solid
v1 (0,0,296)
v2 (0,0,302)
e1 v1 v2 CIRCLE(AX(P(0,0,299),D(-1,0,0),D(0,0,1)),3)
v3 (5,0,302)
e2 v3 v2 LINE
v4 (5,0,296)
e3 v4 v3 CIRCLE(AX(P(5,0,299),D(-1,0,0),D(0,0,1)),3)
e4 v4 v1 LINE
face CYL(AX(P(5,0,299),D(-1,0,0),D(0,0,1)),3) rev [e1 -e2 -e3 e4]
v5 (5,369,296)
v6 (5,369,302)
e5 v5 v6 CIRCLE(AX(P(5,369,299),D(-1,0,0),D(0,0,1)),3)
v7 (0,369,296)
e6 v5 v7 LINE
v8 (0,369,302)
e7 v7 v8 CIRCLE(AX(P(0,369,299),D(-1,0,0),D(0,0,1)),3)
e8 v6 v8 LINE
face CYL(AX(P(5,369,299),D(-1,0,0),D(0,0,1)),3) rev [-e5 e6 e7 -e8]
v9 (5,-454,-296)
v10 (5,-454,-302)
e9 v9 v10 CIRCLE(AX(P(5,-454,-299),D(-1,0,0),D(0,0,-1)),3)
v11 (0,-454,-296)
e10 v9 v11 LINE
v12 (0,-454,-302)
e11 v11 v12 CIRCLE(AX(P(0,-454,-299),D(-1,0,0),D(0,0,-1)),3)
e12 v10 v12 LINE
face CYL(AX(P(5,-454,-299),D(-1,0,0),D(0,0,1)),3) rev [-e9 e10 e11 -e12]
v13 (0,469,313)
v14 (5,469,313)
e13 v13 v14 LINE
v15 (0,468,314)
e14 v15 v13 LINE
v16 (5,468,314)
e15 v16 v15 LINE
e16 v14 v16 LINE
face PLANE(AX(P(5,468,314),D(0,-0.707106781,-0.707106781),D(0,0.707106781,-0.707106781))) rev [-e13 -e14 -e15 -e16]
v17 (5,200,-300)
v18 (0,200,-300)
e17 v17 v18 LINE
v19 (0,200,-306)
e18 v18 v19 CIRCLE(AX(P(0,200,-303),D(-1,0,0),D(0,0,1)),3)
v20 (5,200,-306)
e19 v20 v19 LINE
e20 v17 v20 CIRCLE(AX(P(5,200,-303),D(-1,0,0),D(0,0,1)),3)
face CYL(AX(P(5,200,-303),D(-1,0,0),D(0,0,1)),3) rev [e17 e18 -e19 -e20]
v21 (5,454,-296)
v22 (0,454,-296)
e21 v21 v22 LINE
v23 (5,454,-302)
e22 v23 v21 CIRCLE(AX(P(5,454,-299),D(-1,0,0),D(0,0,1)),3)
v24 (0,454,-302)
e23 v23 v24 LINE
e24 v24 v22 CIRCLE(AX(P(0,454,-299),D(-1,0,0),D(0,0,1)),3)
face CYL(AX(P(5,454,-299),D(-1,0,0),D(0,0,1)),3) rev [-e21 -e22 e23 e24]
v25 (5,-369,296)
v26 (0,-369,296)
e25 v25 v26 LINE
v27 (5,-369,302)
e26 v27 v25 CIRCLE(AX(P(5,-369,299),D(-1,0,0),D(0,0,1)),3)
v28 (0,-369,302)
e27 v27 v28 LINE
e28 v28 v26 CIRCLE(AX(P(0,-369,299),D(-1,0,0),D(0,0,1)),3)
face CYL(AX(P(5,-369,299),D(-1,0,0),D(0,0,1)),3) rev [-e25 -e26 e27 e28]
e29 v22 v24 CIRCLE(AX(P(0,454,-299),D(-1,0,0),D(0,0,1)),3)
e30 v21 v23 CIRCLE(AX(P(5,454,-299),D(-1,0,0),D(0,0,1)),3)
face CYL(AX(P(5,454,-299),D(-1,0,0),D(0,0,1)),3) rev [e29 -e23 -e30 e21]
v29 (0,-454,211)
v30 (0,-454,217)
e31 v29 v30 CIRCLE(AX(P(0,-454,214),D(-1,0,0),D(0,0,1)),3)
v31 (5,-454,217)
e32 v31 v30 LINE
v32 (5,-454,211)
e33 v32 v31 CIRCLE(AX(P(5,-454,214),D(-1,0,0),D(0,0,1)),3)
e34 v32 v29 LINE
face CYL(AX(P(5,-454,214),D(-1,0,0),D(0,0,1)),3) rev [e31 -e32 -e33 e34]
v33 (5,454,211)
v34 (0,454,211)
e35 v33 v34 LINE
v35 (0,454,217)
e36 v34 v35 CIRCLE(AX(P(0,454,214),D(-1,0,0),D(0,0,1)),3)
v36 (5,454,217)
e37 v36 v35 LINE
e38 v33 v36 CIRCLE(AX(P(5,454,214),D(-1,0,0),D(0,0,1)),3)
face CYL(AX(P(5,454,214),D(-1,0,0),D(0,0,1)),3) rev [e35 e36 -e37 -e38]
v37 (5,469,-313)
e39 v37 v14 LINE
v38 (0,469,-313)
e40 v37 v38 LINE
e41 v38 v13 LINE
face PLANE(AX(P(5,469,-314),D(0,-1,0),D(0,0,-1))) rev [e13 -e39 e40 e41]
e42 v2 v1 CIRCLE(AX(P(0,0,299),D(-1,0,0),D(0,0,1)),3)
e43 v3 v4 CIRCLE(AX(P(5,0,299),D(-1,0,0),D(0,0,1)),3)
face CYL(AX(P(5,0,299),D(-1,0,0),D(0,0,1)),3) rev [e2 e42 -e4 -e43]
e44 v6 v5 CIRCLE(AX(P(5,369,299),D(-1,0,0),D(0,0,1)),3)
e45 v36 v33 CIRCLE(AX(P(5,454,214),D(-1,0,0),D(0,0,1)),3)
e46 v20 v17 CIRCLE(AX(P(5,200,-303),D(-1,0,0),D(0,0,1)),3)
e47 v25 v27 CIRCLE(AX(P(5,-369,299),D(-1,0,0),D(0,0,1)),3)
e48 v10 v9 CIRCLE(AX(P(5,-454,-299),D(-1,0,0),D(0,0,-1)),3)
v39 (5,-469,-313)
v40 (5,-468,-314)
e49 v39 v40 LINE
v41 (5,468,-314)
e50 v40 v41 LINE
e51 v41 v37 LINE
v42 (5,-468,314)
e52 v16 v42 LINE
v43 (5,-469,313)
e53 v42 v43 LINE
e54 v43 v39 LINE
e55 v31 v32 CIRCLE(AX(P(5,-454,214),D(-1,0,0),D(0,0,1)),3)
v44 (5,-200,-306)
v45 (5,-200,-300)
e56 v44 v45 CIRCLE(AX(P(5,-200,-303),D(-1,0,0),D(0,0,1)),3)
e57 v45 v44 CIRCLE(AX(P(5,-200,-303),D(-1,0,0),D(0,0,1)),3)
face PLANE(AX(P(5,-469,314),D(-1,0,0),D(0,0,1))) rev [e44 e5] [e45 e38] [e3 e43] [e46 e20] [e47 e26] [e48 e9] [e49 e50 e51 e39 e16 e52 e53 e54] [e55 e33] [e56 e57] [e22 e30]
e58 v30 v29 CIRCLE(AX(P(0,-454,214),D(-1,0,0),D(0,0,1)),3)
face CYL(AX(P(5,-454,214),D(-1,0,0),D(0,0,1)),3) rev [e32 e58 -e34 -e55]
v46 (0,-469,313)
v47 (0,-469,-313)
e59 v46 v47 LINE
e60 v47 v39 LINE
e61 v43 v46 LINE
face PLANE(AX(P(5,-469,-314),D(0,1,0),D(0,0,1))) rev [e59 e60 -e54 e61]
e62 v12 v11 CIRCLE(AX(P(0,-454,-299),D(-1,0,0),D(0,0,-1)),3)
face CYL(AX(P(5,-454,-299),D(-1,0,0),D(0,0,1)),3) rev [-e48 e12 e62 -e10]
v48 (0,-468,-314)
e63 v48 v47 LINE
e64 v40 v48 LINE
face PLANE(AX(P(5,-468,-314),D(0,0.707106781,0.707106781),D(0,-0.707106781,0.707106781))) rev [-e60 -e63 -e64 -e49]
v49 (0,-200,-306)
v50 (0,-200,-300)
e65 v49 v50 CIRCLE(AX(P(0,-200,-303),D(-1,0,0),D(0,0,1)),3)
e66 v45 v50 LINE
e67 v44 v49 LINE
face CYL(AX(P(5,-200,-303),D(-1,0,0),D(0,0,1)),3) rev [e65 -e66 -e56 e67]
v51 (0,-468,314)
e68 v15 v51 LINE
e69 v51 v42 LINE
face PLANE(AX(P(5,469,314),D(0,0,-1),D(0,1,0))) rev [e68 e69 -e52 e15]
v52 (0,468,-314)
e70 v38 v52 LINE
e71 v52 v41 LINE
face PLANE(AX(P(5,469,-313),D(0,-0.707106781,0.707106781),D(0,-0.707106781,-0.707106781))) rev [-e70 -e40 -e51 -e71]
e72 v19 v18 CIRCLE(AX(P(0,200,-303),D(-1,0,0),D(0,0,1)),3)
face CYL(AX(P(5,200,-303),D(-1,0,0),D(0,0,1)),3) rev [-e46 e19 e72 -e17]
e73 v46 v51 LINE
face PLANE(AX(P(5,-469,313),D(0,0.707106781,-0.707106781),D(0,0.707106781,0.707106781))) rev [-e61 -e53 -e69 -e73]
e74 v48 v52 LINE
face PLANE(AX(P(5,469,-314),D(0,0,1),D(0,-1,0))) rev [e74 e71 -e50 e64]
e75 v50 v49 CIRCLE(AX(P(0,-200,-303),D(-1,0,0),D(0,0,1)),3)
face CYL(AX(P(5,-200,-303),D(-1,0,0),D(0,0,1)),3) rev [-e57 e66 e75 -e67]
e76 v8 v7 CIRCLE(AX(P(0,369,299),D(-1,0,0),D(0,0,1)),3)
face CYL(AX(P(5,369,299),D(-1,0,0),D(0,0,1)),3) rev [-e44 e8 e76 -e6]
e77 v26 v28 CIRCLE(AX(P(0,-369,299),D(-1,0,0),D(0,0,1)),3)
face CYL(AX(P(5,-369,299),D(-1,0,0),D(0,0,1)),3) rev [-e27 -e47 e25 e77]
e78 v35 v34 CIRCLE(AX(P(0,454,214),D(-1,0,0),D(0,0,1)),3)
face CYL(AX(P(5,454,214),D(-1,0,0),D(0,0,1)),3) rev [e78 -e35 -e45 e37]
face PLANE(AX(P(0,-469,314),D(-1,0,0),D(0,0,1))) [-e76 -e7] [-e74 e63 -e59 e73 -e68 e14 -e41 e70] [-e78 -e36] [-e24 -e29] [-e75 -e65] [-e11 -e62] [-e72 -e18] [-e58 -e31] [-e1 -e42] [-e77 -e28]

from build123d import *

# Parameters (mm, degrees)
SKETCH_1_W          = 628
SKETCH_1_H          = 938
EXTRUDE_1_DEPTH     = 5
CHAMFER_1_SIZE      = 1
SKETCH_2_R          = 3
CUT_EXTRUDE_1_DEPTH = 565.430686621


with BuildPart() as part:
    # 草图1 → 凸台-拉伸1 (new body)
    with BuildSketch(Plane(origin=(0, 0, 0), x_dir=(0, 0, -1), z_dir=(1, 0, 0))):
        Rectangle(SKETCH_1_W, SKETCH_1_H)
    extrude(amount=EXTRUDE_1_DEPTH)

    # 倒角1
    chamfer_1_edges = [part.edges().sort_by_distance(p)[0] for p in [
        (2.5, 469, 314),
        (2.5, 469, -314),
        (2.5, -469, -314),
        (2.5, -469, 314),
    ]]
    chamfer(chamfer_1_edges, length=CHAMFER_1_SIZE)

    # 草图2 → 切除-拉伸1 (cut, through all)
    with BuildSketch(Plane.ZY):
        with Locations((-299, 454)):
            Circle(SKETCH_2_R)
        with Locations(Location((-299, -454, 0), (0, 0, 180))):
            Circle(SKETCH_2_R)
        with Locations((214, 454)):
            Circle(SKETCH_2_R)
        with Locations((299, 369)):
            Circle(SKETCH_2_R)
        with Locations((299, -369)):
            Circle(SKETCH_2_R)
        with Locations((214, -454)):
            Circle(SKETCH_2_R)
        with Locations((299, 0)):
            Circle(SKETCH_2_R)
        with Locations((-303, 200)):
            Circle(SKETCH_2_R)
        with Locations((-303, -200)):
            Circle(SKETCH_2_R)
    extrude(amount=-CUT_EXTRUDE_1_DEPTH, mode=Mode.SUBTRACT)


solid = part.part
